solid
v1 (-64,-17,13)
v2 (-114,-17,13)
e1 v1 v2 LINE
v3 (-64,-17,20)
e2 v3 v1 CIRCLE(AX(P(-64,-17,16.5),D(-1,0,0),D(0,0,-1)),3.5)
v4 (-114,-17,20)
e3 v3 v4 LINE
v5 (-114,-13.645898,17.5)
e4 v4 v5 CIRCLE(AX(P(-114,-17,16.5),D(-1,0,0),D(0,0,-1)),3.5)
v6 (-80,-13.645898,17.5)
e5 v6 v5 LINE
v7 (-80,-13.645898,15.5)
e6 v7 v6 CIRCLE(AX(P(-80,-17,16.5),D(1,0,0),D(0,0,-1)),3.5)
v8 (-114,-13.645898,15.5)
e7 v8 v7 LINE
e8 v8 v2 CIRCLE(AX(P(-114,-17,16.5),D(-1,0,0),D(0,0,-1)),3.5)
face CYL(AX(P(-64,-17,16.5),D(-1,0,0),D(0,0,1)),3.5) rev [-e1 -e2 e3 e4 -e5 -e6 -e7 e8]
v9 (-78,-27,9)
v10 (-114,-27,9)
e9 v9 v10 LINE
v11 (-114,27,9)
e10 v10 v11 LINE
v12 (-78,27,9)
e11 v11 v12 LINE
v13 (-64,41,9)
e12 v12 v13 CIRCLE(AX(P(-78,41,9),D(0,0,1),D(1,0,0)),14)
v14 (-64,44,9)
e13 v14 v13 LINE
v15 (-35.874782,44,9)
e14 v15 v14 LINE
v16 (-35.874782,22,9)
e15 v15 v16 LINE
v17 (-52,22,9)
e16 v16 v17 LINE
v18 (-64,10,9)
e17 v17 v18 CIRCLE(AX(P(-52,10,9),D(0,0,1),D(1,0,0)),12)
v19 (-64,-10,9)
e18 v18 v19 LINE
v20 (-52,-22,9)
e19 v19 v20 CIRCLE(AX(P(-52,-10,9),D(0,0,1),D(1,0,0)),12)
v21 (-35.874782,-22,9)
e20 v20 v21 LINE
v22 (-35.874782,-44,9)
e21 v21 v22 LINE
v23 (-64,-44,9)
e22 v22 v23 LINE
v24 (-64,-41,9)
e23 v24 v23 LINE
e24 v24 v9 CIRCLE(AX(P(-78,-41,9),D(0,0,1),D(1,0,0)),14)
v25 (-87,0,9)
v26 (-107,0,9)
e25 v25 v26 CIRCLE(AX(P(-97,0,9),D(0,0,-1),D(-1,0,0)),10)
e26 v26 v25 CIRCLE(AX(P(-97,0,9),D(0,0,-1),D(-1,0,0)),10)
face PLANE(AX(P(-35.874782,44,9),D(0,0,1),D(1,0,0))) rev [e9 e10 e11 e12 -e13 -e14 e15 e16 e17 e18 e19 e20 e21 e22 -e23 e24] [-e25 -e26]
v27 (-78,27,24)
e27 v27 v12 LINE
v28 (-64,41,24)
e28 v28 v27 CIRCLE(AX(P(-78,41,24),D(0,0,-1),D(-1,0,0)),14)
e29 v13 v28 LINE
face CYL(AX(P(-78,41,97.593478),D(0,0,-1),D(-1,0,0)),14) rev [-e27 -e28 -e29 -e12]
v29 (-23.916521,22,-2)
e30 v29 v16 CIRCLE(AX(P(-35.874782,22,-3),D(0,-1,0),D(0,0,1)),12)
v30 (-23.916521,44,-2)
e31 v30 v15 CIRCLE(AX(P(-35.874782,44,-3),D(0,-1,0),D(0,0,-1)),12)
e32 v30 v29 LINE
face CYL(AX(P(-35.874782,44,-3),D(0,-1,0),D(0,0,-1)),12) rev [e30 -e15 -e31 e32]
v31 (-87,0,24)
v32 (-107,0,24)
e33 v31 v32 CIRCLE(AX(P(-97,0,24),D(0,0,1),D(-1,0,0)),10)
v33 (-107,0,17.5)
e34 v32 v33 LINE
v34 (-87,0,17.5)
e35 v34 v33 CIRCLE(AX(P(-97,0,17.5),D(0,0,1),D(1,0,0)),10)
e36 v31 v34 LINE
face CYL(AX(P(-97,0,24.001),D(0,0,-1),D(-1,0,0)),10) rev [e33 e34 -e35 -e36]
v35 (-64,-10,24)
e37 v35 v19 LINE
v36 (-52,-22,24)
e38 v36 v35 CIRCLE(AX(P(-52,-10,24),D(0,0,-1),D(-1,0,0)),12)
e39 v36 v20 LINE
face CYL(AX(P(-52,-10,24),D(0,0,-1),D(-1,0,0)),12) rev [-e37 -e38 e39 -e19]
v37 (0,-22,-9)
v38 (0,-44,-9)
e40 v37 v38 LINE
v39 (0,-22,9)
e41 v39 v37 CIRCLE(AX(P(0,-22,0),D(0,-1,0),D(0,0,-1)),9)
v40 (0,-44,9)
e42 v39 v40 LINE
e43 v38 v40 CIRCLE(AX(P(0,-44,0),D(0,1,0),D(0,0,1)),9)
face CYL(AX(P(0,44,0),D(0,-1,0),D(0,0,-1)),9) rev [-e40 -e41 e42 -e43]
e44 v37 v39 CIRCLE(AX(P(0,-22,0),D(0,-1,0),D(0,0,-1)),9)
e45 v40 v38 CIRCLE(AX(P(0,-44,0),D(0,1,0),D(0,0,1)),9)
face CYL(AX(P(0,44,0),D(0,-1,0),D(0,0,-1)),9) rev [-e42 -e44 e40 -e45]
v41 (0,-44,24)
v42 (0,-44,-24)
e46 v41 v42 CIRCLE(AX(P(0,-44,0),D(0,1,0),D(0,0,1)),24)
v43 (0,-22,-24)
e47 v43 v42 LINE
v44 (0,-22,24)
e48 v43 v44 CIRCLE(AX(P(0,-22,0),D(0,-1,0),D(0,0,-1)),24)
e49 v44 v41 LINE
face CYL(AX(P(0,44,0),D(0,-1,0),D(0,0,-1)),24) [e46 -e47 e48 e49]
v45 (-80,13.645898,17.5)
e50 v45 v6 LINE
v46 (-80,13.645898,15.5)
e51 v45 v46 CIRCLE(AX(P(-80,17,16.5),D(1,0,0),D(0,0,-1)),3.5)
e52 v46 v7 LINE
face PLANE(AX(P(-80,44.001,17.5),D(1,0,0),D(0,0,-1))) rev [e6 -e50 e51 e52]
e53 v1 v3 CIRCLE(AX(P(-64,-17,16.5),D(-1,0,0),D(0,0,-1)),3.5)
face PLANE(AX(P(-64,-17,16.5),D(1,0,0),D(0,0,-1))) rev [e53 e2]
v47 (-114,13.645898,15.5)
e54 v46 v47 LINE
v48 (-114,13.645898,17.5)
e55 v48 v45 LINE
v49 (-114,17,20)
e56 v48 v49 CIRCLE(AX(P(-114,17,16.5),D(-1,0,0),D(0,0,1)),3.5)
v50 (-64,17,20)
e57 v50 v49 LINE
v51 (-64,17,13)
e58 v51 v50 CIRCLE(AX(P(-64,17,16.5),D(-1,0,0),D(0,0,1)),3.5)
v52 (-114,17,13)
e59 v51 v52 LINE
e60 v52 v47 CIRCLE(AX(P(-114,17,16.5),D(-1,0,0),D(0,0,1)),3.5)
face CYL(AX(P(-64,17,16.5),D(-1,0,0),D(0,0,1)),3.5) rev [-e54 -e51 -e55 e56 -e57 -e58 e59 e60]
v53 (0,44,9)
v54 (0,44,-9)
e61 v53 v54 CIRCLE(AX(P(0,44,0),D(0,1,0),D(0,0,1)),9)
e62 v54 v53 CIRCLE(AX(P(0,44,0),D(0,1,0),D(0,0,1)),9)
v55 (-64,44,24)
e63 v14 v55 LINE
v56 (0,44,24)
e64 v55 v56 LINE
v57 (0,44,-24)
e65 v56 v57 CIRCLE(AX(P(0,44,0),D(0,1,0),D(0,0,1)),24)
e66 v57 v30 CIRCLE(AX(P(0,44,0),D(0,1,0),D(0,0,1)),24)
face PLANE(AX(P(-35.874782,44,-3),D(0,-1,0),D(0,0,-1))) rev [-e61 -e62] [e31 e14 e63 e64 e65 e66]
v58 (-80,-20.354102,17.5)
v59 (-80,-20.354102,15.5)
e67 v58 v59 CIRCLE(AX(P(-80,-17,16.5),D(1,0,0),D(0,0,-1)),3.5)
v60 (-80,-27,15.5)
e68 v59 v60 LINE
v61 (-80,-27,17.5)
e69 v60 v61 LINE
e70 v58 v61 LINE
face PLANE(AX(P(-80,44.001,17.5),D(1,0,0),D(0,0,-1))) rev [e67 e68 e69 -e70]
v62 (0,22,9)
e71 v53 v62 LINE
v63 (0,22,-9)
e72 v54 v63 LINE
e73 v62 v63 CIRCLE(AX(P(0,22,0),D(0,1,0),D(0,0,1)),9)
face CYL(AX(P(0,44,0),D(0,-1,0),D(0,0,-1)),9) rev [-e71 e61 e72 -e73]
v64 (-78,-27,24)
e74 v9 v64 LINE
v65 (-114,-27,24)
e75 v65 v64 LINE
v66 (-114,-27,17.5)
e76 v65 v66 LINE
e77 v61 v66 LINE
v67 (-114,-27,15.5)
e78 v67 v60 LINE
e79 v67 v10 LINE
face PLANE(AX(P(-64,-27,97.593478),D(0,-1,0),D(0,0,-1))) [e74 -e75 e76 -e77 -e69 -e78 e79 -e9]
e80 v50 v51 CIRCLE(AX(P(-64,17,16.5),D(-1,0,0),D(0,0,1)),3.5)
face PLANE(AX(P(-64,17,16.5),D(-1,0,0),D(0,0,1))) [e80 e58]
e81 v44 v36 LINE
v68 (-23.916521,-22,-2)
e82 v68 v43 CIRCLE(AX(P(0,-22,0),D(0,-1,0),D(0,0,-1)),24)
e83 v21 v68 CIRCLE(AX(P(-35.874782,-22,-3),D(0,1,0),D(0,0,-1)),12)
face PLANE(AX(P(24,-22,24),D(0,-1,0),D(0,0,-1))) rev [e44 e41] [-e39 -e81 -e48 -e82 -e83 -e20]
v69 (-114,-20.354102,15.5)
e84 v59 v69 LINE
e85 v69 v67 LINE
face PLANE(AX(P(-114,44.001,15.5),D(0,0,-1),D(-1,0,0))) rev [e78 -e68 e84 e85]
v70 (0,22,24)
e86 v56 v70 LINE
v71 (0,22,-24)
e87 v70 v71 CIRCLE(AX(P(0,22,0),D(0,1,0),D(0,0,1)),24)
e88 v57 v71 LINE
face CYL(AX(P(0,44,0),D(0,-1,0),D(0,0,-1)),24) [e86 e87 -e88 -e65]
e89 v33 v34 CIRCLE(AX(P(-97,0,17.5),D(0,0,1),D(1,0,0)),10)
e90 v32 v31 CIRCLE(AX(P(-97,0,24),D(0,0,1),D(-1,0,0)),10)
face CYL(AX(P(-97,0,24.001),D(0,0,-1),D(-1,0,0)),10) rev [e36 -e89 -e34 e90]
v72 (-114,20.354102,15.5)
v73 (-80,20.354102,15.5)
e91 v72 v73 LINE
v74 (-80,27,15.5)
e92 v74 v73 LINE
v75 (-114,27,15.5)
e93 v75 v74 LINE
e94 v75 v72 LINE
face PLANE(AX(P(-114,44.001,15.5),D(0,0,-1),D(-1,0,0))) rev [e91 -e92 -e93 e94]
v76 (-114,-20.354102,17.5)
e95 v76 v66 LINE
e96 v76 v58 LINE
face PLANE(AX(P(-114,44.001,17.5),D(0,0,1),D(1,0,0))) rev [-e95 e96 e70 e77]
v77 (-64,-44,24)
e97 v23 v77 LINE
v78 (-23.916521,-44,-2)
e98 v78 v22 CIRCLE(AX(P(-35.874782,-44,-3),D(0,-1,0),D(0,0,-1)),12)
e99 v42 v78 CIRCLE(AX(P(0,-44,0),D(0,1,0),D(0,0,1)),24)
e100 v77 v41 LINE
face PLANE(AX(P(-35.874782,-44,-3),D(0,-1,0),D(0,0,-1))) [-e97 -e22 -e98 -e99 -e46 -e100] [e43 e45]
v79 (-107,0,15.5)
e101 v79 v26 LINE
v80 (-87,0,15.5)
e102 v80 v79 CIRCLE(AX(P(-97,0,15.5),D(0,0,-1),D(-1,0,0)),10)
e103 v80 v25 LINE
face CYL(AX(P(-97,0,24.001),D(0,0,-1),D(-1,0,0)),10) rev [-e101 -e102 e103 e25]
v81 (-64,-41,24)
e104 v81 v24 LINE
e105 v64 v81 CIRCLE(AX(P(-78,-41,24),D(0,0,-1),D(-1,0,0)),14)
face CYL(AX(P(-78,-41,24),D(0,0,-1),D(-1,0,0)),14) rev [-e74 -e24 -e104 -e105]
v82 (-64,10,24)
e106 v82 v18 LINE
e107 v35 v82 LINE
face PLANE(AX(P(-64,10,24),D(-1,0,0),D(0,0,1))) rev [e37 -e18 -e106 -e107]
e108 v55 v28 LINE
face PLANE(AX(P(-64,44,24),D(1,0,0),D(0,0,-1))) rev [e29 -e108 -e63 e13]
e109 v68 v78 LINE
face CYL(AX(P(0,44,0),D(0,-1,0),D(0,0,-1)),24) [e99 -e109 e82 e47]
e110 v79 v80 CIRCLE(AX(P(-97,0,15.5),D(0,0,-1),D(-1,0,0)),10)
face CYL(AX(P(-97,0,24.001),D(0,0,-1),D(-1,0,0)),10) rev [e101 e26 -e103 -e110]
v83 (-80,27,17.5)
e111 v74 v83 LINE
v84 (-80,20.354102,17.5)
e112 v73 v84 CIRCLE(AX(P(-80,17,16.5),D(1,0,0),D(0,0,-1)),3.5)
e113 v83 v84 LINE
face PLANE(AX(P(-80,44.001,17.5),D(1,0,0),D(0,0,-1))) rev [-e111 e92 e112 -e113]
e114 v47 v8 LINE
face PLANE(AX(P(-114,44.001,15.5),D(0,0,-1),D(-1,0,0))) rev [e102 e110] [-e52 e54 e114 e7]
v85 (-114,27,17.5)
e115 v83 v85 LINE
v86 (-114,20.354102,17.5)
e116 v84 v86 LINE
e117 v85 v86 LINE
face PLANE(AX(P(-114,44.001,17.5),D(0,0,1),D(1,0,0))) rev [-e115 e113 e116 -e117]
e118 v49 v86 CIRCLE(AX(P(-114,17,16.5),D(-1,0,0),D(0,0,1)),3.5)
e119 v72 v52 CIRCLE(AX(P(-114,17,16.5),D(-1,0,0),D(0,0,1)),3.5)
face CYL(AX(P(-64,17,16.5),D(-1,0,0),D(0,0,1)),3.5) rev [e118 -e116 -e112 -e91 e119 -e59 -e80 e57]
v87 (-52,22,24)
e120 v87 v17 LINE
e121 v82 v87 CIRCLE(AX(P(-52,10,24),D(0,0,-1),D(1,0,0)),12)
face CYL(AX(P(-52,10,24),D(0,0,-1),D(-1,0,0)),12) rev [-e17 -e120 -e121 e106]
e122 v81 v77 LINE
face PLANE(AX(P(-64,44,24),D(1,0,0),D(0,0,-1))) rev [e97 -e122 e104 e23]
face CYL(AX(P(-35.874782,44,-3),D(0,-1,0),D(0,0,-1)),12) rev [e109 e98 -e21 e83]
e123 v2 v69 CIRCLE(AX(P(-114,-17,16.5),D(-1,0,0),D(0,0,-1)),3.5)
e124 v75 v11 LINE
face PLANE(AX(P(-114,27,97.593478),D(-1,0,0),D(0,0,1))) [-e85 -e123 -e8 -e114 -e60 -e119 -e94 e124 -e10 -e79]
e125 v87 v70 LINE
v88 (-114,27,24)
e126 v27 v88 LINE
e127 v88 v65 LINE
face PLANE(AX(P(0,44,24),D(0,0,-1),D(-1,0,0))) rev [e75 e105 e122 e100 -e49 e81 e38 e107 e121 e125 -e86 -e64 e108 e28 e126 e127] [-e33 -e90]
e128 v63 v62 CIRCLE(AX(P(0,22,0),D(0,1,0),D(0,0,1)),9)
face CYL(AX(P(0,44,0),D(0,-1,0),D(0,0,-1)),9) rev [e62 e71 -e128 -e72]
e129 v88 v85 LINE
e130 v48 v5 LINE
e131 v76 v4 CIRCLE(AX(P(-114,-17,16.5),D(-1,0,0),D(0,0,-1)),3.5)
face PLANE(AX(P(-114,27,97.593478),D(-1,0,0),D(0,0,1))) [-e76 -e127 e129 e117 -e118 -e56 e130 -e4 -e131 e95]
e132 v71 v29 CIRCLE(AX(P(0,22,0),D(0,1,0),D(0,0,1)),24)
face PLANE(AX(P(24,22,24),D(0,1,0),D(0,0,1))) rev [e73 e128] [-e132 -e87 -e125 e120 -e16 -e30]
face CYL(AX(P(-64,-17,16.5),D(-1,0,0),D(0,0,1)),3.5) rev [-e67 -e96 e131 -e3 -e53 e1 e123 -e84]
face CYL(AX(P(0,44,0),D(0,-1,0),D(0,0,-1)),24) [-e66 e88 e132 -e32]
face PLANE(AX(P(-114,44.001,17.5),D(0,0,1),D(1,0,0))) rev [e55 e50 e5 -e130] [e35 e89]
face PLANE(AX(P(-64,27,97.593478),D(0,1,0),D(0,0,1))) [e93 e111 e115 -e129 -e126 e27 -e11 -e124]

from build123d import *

# Parameters (mm, degrees)
FORK_BODY_PROFILE_SKETCH_R      = 9
FORK_BODY_DEPTH                 = 44
OFFSET_TANG_SKETCH_W            = 50
OFFSET_TANG_SKETCH_H            = 54
OFFSET_TANG_DEPTH               = 15
TANG_CROSS_HOLE_REACH           = 128.574
TANG_CROSS_HOLE_SKETCH_R        = 10
TANG_SLOT_2MM_REACH             = 138.429
TANG_SLOT_SKETCH_W              = 34
TANG_SLOT_SKETCH_H              = 2
FORK_ROOT_FILLET_R14_R          = 14
SIDE_RELIEF_SKETCH_R            = 3.5
SIDE_RELIEF_CUT_DEPTH           = 50
FORK_EYE_PROFILE_CUT_DEPTH      = 127.574088976
FORK_EYE_PROFILE_CUT_DEPTH_BACK = 127.574088976


with BuildPart() as part:
    # Fork Body Profile Sketch → Fork Body (new, symmetric)
    with BuildSketch(Plane(origin=(0, 0, 0), x_dir=(1, 0, 0), z_dir=(0, 1, 0))):
        with BuildLine():
            Line((0, -24), (-64, -24))
            Line((-64, -24), (-64, -9))
            Line((-64, -9), (-35.874782229, -9))
            ThreePointArc((-35.874782229, -9), (-27.750743825, -5.831760866), (-23.916521486, 2))
            ThreePointArc((-23.916521486, 2), (17.663521733, 16.248076809), (0, -24))
        make_face()
        with Locations(Location((0, 0, 0), (0, 0, 270))):
            Circle(FORK_BODY_PROFILE_SKETCH_R, mode=Mode.SUBTRACT)
    extrude(amount=FORK_BODY_DEPTH, both=True)

    # Offset Tang Sketch → Offset Tang (add)
    with BuildSketch(Plane(origin=(0, 0, 9), x_dir=(-1, 0, 0), z_dir=(0, 0, -1))):
        with Locations((89, 0)):
            Rectangle(OFFSET_TANG_SKETCH_W, OFFSET_TANG_SKETCH_H)
    extrude(amount=-OFFSET_TANG_DEPTH)

    # Tang Cross Hole Sketch → Tang Cross Hole (cut, up to next)
    with BuildSketch(Plane(origin=(0, 0, 9), x_dir=(-1, 0, 0), z_dir=(0, 0, -1)), mode=Mode.PRIVATE) as tang_cross_hole_sk1:
        with Locations((97, 0)):
            Circle(TANG_CROSS_HOLE_SKETCH_R)
    tang_cross_hole_tool1 = extrude(tang_cross_hole_sk1.sketch, amount=-TANG_CROSS_HOLE_REACH, mode=Mode.PRIVATE) & part.part
    add(tang_cross_hole_tool1.solids().sort_by_distance((-97, 0, 9))[0], mode=Mode.SUBTRACT)

    # Tang Slot Sketch → Tang Slot 2mm (cut, up to next)
    with BuildSketch(Plane.XZ.offset(27), mode=Mode.PRIVATE) as tang_slot_2mm_sk1:
        with Locations((-97, 16.5)):
            Rectangle(TANG_SLOT_SKETCH_W, TANG_SLOT_SKETCH_H)
    tang_slot_2mm_tool1 = extrude(tang_slot_2mm_sk1.sketch, amount=-TANG_SLOT_2MM_REACH, mode=Mode.PRIVATE) & part.part
    add(tang_slot_2mm_tool1.solids().sort_by_distance((-97, -27, 16.5))[0], mode=Mode.SUBTRACT)

    # Fork Root Fillet R14
    fork_root_fillet_r14_edges = [part.edges().sort_by_distance(p)[0] for p in [
        (-64, -27, 16.5),
        (-64, 27, 16.5),
    ]]
    fillet(fork_root_fillet_r14_edges, radius=FORK_ROOT_FILLET_R14_R)

    # Side Relief Sketch → Side Relief Cut (cut)
    with BuildSketch(Plane.ZY.offset(114)):
        with Locations((16.5, 17)):
            Circle(SIDE_RELIEF_SKETCH_R)
        with Locations(Location((16.5, -17, 0), (0, 0, 73.398450401))):
            Circle(SIDE_RELIEF_SKETCH_R)
    extrude(amount=-SIDE_RELIEF_CUT_DEPTH, mode=Mode.SUBTRACT)

    # Fork Eye Profile Sketch → Fork Eye Profile Cut (cut, two sides: drawn at the far end of the back side and taken through both)
    with BuildSketch(Plane(origin=(0, 0, 9), x_dir=(-1, 0, 0), z_dir=(0, 0, -1)).offset(-FORK_EYE_PROFILE_CUT_DEPTH_BACK)):
        with BuildLine():
            Line((-24, 22), (52, 22))
            ThreePointArc((52, 22), (60.485281374, 18.485281374), (64, 10))
            Line((64, 10), (64, -10))
            ThreePointArc((64, -10), (60.485281374, -18.485281374), (52, -22))
            Line((52, -22), (-24, -22))
            Line((-24, -22), (-24, 22))
        make_face()
    extrude(amount=FORK_EYE_PROFILE_CUT_DEPTH + FORK_EYE_PROFILE_CUT_DEPTH_BACK, mode=Mode.SUBTRACT)


solid = part.part
